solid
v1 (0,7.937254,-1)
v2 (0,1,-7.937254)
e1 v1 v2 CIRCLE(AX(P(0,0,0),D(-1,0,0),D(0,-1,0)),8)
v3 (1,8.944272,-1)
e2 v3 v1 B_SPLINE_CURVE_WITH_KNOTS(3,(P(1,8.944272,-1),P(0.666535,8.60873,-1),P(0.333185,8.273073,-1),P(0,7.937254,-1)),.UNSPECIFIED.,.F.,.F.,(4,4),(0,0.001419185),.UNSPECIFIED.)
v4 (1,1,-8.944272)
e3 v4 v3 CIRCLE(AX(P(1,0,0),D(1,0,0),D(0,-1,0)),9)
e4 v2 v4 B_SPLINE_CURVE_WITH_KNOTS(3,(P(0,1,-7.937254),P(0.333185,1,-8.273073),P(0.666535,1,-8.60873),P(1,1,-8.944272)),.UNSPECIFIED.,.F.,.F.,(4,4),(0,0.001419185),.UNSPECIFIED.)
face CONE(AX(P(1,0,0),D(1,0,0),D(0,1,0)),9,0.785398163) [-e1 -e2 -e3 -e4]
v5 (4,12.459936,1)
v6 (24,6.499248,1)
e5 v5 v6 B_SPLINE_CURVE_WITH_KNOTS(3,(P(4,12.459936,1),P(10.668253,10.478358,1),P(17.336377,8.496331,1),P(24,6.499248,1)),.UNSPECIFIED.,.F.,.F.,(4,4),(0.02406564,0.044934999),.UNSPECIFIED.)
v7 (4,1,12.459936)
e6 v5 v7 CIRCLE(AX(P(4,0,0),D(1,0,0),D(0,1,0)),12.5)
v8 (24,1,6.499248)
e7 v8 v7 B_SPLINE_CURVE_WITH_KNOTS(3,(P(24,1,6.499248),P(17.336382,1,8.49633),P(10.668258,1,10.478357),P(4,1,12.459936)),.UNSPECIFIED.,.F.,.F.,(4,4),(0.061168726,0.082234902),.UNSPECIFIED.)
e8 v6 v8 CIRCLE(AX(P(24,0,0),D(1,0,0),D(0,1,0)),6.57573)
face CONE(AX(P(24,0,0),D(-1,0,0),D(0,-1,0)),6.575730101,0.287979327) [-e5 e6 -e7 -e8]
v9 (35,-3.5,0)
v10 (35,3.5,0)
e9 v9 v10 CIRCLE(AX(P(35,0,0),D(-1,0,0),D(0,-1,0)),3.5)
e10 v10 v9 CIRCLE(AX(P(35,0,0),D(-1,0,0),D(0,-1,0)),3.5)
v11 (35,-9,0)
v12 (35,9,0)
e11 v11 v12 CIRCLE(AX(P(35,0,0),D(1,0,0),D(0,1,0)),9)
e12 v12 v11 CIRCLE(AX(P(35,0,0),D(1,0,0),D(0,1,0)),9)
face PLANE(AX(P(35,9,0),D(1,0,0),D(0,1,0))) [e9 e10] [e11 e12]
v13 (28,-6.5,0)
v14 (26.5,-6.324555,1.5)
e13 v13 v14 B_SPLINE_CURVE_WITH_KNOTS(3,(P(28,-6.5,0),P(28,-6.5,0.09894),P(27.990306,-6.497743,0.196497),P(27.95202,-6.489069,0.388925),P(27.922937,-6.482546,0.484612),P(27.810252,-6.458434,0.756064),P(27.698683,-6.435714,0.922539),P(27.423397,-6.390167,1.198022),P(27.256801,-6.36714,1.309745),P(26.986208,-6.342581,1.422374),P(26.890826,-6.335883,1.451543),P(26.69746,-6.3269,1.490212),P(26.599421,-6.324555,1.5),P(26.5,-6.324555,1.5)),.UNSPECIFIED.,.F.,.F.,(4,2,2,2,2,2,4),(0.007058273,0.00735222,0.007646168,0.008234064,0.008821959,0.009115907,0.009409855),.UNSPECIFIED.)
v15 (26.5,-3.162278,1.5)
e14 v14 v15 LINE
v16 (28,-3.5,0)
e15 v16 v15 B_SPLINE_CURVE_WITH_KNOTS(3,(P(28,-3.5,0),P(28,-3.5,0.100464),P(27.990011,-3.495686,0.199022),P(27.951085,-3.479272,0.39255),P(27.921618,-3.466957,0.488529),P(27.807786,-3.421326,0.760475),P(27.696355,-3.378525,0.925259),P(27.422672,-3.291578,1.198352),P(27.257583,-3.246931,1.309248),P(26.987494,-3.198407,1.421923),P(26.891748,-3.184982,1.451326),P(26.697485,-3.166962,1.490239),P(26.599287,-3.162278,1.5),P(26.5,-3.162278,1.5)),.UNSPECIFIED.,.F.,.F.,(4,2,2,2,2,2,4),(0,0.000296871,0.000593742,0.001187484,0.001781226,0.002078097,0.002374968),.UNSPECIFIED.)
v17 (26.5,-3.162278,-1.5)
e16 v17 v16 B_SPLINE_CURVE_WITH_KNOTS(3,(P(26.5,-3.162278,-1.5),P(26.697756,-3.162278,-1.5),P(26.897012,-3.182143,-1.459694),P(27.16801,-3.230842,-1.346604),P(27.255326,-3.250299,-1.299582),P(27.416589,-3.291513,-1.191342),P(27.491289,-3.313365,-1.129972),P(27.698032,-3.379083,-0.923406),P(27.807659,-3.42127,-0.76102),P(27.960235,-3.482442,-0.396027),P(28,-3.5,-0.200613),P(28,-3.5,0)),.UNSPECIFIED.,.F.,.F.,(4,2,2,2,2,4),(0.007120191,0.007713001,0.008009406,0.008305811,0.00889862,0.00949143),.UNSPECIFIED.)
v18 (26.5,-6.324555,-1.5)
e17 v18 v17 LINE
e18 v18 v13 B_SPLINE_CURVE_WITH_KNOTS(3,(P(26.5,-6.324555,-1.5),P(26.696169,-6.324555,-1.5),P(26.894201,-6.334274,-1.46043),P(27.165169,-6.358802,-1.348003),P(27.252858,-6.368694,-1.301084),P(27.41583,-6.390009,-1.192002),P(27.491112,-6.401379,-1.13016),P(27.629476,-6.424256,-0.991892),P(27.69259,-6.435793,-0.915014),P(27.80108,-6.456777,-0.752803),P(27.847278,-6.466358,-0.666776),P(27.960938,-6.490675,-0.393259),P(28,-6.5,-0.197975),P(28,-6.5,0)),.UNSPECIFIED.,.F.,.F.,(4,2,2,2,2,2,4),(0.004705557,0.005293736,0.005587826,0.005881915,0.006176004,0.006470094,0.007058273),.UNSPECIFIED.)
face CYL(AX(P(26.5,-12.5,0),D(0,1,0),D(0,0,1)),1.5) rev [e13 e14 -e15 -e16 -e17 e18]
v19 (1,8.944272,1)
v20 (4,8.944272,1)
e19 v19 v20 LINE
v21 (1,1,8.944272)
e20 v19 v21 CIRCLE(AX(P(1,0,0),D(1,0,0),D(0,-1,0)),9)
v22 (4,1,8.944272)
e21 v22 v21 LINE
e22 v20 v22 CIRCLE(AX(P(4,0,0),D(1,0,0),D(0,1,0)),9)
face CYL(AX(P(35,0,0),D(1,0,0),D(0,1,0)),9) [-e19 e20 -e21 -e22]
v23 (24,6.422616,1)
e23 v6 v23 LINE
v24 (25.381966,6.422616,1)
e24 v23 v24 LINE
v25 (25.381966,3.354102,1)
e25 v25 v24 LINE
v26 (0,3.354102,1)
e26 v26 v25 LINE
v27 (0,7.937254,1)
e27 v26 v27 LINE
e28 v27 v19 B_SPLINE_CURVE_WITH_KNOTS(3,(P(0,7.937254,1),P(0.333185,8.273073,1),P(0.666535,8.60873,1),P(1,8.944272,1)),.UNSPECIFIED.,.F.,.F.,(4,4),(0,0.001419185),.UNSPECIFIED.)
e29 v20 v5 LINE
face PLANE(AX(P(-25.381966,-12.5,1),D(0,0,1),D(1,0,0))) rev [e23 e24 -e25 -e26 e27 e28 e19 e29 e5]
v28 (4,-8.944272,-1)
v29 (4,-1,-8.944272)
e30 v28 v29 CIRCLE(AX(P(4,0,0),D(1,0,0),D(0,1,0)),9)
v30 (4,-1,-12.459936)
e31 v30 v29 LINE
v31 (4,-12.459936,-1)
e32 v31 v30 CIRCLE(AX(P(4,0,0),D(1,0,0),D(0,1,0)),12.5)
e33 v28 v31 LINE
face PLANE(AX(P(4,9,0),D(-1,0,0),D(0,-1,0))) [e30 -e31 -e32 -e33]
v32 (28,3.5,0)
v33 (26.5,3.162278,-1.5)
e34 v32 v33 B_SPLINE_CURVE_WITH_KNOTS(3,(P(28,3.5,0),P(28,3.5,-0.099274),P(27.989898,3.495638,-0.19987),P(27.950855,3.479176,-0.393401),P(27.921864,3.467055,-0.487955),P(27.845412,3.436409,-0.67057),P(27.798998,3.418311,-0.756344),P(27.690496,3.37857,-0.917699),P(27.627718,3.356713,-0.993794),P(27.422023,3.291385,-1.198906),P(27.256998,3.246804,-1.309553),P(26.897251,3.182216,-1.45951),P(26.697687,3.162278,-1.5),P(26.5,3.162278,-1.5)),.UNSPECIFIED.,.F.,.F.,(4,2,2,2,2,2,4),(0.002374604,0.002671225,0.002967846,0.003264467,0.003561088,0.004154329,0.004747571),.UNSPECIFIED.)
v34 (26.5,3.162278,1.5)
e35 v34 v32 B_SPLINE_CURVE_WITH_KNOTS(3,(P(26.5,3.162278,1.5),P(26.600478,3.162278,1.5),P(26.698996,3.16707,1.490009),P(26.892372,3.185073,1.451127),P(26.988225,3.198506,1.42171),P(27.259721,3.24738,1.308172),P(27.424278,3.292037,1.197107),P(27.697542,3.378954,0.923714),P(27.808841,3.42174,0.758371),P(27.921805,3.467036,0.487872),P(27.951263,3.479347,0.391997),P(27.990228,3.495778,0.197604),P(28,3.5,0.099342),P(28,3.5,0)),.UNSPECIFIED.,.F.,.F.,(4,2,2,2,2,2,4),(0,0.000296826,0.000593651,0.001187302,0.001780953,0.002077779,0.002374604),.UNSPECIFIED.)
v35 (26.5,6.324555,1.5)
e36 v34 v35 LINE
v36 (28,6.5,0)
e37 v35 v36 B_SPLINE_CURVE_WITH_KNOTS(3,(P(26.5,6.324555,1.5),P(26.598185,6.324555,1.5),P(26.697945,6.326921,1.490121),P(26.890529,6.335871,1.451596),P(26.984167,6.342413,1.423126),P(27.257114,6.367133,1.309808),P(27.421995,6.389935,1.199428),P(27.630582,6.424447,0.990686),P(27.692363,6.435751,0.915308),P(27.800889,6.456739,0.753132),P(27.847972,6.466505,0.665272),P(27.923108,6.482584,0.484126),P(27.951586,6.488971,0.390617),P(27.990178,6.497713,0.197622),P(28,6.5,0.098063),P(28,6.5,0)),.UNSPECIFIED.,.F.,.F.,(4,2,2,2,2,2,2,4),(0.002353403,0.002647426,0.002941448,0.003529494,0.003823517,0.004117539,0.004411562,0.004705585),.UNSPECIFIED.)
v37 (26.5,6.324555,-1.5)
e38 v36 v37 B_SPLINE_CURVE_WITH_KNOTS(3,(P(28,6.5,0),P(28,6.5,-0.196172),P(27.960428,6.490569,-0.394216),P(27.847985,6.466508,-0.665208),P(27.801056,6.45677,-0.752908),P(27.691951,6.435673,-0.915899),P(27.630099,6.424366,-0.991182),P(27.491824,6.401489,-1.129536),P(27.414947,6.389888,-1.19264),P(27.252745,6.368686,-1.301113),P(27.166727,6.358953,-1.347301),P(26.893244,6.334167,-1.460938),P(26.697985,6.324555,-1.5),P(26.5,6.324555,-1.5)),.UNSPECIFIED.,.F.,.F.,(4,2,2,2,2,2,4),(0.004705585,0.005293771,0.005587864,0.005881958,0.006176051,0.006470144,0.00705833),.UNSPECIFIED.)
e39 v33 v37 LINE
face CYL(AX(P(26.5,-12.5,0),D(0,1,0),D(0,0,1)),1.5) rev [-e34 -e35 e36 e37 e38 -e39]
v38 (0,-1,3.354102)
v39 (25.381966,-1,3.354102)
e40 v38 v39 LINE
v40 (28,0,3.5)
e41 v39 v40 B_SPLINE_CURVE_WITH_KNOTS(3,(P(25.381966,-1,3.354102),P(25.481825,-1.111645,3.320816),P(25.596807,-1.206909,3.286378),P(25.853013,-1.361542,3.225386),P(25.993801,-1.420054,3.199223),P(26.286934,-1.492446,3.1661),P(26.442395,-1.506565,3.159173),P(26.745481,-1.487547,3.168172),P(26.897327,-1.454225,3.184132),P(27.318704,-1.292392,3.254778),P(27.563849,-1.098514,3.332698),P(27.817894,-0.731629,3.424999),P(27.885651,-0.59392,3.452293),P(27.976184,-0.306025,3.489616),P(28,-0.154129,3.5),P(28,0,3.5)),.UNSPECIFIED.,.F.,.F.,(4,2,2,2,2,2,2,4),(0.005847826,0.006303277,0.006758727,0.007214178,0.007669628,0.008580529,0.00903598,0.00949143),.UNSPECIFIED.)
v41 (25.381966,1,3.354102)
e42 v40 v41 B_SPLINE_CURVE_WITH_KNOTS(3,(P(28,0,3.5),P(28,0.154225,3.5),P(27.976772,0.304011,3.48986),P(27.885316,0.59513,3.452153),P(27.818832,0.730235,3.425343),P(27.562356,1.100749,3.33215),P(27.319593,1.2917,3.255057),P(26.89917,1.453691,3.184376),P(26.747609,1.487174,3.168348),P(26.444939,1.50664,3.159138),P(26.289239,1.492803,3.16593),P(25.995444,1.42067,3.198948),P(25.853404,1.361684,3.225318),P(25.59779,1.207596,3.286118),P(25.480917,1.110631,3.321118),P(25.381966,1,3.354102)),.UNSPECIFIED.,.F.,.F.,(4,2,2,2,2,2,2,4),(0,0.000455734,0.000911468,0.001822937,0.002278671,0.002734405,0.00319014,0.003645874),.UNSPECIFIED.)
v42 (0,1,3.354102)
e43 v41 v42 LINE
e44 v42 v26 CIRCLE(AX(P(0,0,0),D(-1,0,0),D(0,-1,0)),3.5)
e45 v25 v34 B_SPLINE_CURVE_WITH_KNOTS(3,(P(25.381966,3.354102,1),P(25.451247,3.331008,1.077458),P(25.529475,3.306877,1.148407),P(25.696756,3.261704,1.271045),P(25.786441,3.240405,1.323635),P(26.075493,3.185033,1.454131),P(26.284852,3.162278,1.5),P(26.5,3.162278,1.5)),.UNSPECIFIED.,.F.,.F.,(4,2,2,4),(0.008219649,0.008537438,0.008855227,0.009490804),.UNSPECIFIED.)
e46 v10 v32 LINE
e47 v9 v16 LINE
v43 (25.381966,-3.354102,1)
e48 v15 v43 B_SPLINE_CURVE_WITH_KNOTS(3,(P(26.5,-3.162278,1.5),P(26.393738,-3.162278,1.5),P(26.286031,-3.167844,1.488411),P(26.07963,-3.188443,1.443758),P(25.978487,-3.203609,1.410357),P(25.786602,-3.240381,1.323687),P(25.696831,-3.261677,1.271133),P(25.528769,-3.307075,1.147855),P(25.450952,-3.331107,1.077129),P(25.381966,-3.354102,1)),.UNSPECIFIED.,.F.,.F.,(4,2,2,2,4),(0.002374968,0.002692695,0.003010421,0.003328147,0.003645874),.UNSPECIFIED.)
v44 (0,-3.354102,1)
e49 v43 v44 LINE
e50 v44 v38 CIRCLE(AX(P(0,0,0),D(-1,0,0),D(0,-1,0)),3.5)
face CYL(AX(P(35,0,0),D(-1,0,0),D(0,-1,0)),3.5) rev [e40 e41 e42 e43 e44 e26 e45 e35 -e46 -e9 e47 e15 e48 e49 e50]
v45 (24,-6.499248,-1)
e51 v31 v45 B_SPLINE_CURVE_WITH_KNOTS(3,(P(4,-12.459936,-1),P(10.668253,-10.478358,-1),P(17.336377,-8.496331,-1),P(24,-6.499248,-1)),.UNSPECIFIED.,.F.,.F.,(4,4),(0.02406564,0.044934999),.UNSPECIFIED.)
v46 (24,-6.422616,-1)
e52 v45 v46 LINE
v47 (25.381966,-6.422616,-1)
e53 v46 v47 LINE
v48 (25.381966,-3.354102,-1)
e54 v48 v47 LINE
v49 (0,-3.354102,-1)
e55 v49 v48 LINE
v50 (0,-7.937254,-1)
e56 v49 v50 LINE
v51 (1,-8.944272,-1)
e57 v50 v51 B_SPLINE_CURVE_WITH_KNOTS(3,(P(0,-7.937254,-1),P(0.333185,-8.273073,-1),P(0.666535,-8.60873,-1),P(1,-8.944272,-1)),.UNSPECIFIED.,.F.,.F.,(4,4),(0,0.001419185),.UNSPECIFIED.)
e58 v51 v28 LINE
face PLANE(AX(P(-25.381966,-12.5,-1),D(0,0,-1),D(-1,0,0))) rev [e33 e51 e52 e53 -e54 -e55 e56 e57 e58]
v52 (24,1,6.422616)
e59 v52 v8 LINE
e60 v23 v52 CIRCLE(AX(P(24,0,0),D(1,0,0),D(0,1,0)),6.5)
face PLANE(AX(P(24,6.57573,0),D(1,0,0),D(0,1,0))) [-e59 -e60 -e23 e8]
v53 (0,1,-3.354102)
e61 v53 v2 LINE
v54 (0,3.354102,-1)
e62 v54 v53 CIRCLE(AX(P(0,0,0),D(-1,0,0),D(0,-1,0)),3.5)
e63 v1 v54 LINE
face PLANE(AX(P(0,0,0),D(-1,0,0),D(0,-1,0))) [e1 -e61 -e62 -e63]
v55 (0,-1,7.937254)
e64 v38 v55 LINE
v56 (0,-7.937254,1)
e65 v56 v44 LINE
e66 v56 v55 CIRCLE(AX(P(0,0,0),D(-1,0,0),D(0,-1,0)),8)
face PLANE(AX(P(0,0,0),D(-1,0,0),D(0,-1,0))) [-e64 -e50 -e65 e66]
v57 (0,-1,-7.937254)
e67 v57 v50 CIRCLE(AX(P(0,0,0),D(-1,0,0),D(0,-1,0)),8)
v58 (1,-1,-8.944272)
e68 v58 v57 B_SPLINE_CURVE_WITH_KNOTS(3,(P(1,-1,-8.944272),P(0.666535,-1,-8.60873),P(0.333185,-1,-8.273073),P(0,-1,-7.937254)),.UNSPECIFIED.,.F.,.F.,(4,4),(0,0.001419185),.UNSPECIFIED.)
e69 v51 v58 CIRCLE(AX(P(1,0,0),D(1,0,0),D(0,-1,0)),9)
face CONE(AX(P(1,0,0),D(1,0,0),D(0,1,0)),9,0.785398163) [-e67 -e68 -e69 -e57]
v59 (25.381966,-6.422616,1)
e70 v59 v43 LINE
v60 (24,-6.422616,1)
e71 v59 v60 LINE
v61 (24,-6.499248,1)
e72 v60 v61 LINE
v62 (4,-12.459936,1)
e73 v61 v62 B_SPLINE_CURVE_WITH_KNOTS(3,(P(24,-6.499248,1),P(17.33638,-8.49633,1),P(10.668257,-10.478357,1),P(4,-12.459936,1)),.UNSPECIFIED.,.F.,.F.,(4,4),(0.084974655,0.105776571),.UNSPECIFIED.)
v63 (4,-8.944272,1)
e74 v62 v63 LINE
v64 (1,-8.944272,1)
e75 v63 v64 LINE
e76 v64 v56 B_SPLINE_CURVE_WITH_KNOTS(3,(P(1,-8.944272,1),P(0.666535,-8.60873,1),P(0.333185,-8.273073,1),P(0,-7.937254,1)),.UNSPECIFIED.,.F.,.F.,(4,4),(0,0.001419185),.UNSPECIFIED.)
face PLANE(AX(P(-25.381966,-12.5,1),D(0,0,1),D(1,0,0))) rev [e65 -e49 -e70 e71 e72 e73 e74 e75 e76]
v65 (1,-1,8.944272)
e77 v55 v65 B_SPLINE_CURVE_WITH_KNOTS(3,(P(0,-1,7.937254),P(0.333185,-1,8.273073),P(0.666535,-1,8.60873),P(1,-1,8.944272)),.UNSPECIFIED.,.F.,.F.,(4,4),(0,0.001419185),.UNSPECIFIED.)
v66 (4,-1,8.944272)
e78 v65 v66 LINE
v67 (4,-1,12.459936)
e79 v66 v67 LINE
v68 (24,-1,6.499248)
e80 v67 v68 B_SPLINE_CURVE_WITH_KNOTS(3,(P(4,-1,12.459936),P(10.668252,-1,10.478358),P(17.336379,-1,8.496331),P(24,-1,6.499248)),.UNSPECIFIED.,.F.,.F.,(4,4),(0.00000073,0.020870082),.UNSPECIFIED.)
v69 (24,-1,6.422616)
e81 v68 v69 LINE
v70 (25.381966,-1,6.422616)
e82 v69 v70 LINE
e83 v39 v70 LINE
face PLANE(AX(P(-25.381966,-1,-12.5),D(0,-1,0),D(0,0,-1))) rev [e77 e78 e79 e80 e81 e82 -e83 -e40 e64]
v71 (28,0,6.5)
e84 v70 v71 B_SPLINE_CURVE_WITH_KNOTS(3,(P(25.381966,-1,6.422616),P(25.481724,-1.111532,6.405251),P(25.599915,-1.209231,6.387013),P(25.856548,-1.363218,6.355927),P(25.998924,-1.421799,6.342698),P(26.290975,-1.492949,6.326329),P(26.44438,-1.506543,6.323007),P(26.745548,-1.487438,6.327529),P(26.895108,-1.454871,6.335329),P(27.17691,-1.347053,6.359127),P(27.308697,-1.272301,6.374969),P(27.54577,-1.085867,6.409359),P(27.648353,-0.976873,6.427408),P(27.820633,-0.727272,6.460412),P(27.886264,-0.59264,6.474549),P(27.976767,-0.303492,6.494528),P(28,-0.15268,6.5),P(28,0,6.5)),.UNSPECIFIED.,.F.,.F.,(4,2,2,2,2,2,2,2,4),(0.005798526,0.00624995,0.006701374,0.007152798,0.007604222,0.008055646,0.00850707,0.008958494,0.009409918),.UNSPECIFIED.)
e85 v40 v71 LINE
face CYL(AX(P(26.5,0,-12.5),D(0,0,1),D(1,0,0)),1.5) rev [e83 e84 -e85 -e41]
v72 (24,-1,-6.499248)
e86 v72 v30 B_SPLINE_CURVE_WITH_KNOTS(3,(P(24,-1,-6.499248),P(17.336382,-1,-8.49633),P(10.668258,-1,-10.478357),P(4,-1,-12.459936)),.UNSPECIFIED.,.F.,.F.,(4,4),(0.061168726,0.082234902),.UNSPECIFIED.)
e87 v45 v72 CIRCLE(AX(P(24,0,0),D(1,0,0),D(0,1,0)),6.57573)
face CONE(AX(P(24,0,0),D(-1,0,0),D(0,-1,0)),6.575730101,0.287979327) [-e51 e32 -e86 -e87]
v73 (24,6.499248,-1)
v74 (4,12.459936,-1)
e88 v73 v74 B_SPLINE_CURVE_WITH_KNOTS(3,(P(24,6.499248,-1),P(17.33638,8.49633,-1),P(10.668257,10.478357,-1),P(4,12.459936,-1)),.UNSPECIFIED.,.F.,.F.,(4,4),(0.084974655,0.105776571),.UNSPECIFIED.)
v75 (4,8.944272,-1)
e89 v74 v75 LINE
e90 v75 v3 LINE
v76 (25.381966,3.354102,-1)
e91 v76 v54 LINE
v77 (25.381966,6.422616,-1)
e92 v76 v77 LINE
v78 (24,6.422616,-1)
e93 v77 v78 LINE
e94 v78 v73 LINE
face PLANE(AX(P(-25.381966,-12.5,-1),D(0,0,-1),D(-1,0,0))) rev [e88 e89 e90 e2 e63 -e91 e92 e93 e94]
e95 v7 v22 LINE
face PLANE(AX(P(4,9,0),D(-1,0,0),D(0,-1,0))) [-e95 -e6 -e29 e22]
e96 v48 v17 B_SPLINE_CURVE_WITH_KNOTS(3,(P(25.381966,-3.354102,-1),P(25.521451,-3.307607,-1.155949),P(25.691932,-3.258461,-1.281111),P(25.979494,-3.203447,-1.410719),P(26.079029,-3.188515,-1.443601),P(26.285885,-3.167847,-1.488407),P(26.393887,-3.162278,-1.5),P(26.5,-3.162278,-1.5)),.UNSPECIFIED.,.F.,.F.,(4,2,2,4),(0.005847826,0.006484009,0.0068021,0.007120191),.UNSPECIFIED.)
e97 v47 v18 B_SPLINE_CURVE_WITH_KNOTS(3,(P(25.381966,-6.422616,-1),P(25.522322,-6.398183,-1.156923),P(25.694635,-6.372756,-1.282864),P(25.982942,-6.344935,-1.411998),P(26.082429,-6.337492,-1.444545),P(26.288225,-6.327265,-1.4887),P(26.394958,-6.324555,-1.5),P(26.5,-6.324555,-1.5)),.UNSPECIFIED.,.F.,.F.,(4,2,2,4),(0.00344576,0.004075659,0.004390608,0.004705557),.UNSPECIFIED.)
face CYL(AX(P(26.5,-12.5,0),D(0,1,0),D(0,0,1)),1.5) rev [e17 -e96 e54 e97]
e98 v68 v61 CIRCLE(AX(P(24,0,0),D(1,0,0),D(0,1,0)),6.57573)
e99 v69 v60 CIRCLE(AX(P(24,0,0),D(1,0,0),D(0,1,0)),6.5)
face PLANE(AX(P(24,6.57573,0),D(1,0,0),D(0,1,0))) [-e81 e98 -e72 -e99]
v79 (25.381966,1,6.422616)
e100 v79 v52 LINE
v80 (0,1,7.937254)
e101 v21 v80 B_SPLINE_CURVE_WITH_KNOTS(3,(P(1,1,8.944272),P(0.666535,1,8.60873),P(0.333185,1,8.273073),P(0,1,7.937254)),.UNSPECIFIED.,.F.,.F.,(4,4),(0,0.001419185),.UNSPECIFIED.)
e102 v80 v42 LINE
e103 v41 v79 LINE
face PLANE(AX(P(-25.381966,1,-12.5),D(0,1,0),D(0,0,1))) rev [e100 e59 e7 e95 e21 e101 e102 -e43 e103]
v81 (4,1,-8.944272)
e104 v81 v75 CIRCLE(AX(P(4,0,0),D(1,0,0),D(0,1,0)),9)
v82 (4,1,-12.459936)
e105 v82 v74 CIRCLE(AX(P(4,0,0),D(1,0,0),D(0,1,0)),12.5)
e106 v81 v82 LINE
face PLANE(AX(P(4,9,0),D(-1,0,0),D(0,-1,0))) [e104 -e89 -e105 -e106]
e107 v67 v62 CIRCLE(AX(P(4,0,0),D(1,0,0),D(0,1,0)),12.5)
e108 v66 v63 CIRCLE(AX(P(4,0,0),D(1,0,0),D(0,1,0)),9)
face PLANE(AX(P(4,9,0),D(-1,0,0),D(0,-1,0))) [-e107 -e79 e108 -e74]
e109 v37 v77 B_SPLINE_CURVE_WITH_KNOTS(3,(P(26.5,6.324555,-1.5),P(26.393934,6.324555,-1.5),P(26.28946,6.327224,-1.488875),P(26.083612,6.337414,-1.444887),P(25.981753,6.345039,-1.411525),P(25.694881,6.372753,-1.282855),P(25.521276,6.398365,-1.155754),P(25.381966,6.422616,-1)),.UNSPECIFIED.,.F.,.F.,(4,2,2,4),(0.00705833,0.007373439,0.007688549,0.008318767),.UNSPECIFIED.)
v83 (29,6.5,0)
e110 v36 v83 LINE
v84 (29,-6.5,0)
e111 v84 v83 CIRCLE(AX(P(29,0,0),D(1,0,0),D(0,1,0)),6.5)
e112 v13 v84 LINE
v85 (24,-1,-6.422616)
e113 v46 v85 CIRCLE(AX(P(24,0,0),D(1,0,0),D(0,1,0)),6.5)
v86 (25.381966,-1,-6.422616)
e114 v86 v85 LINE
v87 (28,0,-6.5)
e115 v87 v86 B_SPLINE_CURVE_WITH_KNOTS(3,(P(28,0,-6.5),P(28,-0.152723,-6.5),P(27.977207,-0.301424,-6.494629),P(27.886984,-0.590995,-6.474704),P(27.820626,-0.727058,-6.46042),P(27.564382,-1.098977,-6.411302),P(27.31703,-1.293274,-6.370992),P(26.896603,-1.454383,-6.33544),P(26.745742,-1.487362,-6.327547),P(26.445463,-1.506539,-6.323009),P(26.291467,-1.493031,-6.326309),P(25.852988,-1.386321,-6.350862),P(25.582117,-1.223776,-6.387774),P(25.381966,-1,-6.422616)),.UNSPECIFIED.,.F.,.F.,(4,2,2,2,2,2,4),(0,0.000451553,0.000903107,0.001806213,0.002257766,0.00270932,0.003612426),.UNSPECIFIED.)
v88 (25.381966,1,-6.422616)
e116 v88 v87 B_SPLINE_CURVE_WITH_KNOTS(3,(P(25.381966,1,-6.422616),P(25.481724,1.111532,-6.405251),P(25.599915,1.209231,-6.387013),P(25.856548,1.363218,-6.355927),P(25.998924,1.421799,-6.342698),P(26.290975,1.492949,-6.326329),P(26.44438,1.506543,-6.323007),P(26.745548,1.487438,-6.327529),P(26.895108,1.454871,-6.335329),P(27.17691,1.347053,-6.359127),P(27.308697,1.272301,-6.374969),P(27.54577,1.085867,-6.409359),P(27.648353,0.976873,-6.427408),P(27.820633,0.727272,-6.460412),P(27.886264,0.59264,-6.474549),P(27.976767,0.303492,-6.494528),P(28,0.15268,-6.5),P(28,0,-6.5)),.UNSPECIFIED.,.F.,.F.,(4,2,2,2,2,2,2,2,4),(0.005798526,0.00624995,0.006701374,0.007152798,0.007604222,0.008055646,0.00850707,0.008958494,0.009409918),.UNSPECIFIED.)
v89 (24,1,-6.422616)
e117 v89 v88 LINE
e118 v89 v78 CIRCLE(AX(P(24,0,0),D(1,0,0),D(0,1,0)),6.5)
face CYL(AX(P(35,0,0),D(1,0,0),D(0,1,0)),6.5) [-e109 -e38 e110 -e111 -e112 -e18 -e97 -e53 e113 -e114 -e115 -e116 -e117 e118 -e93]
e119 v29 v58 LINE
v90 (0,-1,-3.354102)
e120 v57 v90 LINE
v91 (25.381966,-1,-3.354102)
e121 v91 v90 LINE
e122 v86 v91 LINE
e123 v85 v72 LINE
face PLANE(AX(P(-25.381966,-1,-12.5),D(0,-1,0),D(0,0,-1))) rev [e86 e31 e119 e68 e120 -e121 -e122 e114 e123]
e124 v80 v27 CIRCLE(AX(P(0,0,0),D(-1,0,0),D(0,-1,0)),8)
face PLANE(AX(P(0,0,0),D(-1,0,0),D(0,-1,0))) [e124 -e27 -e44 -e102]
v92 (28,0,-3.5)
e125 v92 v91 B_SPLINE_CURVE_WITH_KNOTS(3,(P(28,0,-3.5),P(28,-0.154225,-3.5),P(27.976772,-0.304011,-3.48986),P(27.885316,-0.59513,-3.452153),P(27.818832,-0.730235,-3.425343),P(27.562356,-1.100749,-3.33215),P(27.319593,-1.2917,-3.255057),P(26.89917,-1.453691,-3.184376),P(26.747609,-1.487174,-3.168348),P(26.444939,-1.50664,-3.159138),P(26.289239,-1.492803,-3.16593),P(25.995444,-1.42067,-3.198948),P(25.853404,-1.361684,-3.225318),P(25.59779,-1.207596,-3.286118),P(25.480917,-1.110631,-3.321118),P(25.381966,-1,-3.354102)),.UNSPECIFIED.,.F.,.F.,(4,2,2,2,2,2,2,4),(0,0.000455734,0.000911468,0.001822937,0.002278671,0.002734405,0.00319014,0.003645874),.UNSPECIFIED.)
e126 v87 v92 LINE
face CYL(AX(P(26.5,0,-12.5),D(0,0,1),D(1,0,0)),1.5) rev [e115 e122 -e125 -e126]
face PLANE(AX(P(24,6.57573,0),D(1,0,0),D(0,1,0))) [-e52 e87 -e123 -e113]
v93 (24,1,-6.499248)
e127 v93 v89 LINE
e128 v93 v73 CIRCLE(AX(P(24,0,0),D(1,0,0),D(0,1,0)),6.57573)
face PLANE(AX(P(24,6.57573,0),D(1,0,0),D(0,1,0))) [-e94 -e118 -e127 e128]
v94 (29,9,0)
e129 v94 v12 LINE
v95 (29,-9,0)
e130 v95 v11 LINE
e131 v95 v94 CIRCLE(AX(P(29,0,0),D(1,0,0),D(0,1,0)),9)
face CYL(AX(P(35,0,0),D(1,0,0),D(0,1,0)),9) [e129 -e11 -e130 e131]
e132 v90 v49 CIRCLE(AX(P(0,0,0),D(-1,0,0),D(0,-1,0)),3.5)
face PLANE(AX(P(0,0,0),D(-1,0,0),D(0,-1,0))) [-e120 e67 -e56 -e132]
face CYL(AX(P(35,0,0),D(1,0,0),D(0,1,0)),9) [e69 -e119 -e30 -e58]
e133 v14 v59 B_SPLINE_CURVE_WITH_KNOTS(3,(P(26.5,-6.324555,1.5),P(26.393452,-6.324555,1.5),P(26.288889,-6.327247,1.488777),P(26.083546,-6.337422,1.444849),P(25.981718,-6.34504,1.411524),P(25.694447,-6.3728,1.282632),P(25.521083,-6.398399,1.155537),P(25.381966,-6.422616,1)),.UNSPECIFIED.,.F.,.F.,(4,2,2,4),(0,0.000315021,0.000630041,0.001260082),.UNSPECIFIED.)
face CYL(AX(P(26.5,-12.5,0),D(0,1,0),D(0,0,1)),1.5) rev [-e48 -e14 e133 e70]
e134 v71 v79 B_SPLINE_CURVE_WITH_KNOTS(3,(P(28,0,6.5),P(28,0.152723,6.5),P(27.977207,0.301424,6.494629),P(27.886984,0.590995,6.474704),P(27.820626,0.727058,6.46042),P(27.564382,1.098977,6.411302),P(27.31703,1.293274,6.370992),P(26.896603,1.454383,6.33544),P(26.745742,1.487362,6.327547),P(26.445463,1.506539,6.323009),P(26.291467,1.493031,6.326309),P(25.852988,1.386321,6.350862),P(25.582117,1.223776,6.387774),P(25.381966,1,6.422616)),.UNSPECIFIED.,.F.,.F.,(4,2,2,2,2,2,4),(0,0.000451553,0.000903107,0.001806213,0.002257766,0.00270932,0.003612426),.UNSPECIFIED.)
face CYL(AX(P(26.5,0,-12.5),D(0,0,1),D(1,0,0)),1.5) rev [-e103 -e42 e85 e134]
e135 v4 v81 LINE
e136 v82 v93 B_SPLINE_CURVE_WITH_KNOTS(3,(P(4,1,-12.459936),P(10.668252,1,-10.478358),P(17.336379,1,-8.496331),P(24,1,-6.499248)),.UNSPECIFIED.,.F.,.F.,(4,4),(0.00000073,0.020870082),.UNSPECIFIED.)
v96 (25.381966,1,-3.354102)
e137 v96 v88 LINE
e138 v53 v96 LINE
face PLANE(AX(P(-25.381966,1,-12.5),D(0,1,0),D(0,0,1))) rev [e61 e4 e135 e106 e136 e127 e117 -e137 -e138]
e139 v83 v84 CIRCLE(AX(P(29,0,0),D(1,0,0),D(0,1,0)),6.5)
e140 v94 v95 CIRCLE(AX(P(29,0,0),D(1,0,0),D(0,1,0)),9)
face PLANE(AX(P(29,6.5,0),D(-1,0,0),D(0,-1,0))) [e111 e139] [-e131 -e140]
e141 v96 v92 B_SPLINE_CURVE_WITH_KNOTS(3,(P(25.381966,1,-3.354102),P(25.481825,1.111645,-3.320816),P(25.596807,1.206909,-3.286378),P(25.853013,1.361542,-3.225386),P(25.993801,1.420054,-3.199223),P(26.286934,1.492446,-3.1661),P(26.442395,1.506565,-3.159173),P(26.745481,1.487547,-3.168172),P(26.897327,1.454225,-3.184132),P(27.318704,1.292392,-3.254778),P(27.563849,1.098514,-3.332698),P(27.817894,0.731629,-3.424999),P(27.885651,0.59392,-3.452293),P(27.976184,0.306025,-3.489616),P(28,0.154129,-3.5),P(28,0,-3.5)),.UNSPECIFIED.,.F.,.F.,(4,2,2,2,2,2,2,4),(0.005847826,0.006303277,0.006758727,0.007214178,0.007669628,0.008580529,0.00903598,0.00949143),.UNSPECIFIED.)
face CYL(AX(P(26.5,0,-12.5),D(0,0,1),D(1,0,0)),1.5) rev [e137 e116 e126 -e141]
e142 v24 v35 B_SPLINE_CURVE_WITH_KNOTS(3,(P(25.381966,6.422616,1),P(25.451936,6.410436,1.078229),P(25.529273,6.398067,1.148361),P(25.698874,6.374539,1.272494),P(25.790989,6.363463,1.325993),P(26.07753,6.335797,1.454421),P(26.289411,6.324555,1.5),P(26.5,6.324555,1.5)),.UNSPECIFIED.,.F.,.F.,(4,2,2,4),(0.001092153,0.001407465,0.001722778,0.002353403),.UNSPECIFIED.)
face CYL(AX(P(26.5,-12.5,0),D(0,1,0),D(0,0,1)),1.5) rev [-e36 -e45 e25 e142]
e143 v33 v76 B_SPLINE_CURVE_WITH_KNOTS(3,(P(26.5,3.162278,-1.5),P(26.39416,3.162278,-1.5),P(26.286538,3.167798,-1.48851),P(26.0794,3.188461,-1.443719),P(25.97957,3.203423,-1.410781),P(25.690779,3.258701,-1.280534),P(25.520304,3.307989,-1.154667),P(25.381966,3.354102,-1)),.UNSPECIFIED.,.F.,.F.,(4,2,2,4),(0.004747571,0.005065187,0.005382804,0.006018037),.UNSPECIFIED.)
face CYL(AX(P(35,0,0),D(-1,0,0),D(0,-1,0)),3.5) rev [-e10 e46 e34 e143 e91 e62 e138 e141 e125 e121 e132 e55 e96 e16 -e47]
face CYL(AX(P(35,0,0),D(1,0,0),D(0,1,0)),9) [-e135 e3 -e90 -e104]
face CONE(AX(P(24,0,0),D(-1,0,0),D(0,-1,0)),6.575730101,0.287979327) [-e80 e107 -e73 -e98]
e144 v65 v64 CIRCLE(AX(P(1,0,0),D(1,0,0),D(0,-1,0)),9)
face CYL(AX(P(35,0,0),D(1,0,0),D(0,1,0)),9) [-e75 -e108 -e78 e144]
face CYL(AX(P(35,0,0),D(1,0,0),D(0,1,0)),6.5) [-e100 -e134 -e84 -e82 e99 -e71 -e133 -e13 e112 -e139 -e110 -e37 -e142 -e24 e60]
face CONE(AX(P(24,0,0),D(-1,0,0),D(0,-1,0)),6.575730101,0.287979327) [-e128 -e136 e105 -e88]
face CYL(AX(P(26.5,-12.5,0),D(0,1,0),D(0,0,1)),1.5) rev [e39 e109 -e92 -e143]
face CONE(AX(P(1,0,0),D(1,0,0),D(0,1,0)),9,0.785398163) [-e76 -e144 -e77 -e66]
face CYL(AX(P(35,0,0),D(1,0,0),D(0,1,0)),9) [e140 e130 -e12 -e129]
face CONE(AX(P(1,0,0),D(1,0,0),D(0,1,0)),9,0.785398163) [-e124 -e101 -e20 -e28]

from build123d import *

# Parameters (mm, degrees)
SKETCH2_R               = 3.5
CUT_EXTRUDE1_DEPTH      = 40.210967853
CUT_EXTRUDE2_DEPTH      = 40.210967853
CUT_EXTRUDE2_DEPTH_BACK = 40.210967853
SKETCH3_R               = 1.5
CUT_EXTRUDE3_DEPTH      = 40.210967943
CUT_EXTRUDE3_DEPTH_BACK = 40.210967943
SKETCH4_R               = 1.5
CUT_EXTRUDE4_DEPTH      = 40.210967943
CUT_EXTRUDE4_DEPTH_BACK = 40.210967943
SKETCH5_W               = 50.763932022
SKETCH5_H               = 2
CUT_EXTRUDE5_DEPTH      = 40.198214334
CUT_EXTRUDE5_DEPTH_BACK = 40.198214334
SKETCH6_W               = 50.763932022
SKETCH6_H               = 2
CHAMFER1_SIZE           = 1


with BuildPart() as part:
    # Sketch1 → Revolve1 (revolve)
    with BuildSketch(Plane.XY):
        Polygon((0, 0), (0, 9), (4, 9), (4, 12.5), (24, 6.575730101), (24, 6.5), (29, 6.5), (29, 9), (35, 9), (35, 0), align=None)
    revolve(axis=Axis((35, 0, 0), (-1, 0, 0)))

    # Sketch2 → Cut-Extrude1 (cut, through all)
    with BuildSketch(Plane.ZY):
        with Locations(Location((0, 0, 0), (0, 0, 270))):
            Circle(SKETCH2_R)
    extrude(amount=-CUT_EXTRUDE1_DEPTH, mode=Mode.SUBTRACT)

    # Sketch3 → Cut-Extrude2 (cut, two sides: drawn at the far end of the back side and taken through both)
    with BuildSketch(Plane.XY.offset(-CUT_EXTRUDE2_DEPTH_BACK)):
        with Locations((26.5, 0)):
            Circle(SKETCH3_R)
    extrude(amount=CUT_EXTRUDE2_DEPTH + CUT_EXTRUDE2_DEPTH_BACK, mode=Mode.SUBTRACT)

    # Sketch4 → Cut-Extrude3 (cut, two sides: drawn at the far end of the back side and taken through both)
    with BuildSketch(Plane(origin=(0, 0, 0), x_dir=(1, 0, 0), z_dir=(0, 1, 0)).offset(-CUT_EXTRUDE3_DEPTH_BACK)):
        with Locations(Location((26.5, 0, 0), (0, 0, 270))):
            Circle(SKETCH4_R)
    extrude(amount=CUT_EXTRUDE3_DEPTH + CUT_EXTRUDE3_DEPTH_BACK, mode=Mode.SUBTRACT)

    # Sketch5 → Cut-Extrude4 (cut, two sides: drawn at the far end of the back side and taken through both)
    with BuildSketch(Plane.XY.offset(-CUT_EXTRUDE4_DEPTH_BACK)):
        Rectangle(SKETCH5_W, SKETCH5_H)
    extrude(amount=CUT_EXTRUDE4_DEPTH + CUT_EXTRUDE4_DEPTH_BACK, mode=Mode.SUBTRACT)

    # Sketch6 → Cut-Extrude5 (cut, two sides: drawn at the far end of the back side and taken through both)
    with BuildSketch(Plane(origin=(0, 0, 0), x_dir=(1, 0, 0), z_dir=(0, 1, 0)).offset(-CUT_EXTRUDE5_DEPTH_BACK)):
        Rectangle(SKETCH6_W, SKETCH6_H)
    extrude(amount=CUT_EXTRUDE5_DEPTH + CUT_EXTRUDE5_DEPTH_BACK, mode=Mode.SUBTRACT)

    # Chamfer1
    chamfer1_edges = [part.edges().sort_by_distance(p)[0] for p in [
        (0, 6.363961031, 6.363961031),
        (0, -6.363961031, -6.363961031),
        (0, -6.363961031, 6.363961031),
        (0, 6.363961031, -6.363961031),
    ]]
    chamfer(chamfer1_edges, length=CHAMFER1_SIZE)


solid = part.part
